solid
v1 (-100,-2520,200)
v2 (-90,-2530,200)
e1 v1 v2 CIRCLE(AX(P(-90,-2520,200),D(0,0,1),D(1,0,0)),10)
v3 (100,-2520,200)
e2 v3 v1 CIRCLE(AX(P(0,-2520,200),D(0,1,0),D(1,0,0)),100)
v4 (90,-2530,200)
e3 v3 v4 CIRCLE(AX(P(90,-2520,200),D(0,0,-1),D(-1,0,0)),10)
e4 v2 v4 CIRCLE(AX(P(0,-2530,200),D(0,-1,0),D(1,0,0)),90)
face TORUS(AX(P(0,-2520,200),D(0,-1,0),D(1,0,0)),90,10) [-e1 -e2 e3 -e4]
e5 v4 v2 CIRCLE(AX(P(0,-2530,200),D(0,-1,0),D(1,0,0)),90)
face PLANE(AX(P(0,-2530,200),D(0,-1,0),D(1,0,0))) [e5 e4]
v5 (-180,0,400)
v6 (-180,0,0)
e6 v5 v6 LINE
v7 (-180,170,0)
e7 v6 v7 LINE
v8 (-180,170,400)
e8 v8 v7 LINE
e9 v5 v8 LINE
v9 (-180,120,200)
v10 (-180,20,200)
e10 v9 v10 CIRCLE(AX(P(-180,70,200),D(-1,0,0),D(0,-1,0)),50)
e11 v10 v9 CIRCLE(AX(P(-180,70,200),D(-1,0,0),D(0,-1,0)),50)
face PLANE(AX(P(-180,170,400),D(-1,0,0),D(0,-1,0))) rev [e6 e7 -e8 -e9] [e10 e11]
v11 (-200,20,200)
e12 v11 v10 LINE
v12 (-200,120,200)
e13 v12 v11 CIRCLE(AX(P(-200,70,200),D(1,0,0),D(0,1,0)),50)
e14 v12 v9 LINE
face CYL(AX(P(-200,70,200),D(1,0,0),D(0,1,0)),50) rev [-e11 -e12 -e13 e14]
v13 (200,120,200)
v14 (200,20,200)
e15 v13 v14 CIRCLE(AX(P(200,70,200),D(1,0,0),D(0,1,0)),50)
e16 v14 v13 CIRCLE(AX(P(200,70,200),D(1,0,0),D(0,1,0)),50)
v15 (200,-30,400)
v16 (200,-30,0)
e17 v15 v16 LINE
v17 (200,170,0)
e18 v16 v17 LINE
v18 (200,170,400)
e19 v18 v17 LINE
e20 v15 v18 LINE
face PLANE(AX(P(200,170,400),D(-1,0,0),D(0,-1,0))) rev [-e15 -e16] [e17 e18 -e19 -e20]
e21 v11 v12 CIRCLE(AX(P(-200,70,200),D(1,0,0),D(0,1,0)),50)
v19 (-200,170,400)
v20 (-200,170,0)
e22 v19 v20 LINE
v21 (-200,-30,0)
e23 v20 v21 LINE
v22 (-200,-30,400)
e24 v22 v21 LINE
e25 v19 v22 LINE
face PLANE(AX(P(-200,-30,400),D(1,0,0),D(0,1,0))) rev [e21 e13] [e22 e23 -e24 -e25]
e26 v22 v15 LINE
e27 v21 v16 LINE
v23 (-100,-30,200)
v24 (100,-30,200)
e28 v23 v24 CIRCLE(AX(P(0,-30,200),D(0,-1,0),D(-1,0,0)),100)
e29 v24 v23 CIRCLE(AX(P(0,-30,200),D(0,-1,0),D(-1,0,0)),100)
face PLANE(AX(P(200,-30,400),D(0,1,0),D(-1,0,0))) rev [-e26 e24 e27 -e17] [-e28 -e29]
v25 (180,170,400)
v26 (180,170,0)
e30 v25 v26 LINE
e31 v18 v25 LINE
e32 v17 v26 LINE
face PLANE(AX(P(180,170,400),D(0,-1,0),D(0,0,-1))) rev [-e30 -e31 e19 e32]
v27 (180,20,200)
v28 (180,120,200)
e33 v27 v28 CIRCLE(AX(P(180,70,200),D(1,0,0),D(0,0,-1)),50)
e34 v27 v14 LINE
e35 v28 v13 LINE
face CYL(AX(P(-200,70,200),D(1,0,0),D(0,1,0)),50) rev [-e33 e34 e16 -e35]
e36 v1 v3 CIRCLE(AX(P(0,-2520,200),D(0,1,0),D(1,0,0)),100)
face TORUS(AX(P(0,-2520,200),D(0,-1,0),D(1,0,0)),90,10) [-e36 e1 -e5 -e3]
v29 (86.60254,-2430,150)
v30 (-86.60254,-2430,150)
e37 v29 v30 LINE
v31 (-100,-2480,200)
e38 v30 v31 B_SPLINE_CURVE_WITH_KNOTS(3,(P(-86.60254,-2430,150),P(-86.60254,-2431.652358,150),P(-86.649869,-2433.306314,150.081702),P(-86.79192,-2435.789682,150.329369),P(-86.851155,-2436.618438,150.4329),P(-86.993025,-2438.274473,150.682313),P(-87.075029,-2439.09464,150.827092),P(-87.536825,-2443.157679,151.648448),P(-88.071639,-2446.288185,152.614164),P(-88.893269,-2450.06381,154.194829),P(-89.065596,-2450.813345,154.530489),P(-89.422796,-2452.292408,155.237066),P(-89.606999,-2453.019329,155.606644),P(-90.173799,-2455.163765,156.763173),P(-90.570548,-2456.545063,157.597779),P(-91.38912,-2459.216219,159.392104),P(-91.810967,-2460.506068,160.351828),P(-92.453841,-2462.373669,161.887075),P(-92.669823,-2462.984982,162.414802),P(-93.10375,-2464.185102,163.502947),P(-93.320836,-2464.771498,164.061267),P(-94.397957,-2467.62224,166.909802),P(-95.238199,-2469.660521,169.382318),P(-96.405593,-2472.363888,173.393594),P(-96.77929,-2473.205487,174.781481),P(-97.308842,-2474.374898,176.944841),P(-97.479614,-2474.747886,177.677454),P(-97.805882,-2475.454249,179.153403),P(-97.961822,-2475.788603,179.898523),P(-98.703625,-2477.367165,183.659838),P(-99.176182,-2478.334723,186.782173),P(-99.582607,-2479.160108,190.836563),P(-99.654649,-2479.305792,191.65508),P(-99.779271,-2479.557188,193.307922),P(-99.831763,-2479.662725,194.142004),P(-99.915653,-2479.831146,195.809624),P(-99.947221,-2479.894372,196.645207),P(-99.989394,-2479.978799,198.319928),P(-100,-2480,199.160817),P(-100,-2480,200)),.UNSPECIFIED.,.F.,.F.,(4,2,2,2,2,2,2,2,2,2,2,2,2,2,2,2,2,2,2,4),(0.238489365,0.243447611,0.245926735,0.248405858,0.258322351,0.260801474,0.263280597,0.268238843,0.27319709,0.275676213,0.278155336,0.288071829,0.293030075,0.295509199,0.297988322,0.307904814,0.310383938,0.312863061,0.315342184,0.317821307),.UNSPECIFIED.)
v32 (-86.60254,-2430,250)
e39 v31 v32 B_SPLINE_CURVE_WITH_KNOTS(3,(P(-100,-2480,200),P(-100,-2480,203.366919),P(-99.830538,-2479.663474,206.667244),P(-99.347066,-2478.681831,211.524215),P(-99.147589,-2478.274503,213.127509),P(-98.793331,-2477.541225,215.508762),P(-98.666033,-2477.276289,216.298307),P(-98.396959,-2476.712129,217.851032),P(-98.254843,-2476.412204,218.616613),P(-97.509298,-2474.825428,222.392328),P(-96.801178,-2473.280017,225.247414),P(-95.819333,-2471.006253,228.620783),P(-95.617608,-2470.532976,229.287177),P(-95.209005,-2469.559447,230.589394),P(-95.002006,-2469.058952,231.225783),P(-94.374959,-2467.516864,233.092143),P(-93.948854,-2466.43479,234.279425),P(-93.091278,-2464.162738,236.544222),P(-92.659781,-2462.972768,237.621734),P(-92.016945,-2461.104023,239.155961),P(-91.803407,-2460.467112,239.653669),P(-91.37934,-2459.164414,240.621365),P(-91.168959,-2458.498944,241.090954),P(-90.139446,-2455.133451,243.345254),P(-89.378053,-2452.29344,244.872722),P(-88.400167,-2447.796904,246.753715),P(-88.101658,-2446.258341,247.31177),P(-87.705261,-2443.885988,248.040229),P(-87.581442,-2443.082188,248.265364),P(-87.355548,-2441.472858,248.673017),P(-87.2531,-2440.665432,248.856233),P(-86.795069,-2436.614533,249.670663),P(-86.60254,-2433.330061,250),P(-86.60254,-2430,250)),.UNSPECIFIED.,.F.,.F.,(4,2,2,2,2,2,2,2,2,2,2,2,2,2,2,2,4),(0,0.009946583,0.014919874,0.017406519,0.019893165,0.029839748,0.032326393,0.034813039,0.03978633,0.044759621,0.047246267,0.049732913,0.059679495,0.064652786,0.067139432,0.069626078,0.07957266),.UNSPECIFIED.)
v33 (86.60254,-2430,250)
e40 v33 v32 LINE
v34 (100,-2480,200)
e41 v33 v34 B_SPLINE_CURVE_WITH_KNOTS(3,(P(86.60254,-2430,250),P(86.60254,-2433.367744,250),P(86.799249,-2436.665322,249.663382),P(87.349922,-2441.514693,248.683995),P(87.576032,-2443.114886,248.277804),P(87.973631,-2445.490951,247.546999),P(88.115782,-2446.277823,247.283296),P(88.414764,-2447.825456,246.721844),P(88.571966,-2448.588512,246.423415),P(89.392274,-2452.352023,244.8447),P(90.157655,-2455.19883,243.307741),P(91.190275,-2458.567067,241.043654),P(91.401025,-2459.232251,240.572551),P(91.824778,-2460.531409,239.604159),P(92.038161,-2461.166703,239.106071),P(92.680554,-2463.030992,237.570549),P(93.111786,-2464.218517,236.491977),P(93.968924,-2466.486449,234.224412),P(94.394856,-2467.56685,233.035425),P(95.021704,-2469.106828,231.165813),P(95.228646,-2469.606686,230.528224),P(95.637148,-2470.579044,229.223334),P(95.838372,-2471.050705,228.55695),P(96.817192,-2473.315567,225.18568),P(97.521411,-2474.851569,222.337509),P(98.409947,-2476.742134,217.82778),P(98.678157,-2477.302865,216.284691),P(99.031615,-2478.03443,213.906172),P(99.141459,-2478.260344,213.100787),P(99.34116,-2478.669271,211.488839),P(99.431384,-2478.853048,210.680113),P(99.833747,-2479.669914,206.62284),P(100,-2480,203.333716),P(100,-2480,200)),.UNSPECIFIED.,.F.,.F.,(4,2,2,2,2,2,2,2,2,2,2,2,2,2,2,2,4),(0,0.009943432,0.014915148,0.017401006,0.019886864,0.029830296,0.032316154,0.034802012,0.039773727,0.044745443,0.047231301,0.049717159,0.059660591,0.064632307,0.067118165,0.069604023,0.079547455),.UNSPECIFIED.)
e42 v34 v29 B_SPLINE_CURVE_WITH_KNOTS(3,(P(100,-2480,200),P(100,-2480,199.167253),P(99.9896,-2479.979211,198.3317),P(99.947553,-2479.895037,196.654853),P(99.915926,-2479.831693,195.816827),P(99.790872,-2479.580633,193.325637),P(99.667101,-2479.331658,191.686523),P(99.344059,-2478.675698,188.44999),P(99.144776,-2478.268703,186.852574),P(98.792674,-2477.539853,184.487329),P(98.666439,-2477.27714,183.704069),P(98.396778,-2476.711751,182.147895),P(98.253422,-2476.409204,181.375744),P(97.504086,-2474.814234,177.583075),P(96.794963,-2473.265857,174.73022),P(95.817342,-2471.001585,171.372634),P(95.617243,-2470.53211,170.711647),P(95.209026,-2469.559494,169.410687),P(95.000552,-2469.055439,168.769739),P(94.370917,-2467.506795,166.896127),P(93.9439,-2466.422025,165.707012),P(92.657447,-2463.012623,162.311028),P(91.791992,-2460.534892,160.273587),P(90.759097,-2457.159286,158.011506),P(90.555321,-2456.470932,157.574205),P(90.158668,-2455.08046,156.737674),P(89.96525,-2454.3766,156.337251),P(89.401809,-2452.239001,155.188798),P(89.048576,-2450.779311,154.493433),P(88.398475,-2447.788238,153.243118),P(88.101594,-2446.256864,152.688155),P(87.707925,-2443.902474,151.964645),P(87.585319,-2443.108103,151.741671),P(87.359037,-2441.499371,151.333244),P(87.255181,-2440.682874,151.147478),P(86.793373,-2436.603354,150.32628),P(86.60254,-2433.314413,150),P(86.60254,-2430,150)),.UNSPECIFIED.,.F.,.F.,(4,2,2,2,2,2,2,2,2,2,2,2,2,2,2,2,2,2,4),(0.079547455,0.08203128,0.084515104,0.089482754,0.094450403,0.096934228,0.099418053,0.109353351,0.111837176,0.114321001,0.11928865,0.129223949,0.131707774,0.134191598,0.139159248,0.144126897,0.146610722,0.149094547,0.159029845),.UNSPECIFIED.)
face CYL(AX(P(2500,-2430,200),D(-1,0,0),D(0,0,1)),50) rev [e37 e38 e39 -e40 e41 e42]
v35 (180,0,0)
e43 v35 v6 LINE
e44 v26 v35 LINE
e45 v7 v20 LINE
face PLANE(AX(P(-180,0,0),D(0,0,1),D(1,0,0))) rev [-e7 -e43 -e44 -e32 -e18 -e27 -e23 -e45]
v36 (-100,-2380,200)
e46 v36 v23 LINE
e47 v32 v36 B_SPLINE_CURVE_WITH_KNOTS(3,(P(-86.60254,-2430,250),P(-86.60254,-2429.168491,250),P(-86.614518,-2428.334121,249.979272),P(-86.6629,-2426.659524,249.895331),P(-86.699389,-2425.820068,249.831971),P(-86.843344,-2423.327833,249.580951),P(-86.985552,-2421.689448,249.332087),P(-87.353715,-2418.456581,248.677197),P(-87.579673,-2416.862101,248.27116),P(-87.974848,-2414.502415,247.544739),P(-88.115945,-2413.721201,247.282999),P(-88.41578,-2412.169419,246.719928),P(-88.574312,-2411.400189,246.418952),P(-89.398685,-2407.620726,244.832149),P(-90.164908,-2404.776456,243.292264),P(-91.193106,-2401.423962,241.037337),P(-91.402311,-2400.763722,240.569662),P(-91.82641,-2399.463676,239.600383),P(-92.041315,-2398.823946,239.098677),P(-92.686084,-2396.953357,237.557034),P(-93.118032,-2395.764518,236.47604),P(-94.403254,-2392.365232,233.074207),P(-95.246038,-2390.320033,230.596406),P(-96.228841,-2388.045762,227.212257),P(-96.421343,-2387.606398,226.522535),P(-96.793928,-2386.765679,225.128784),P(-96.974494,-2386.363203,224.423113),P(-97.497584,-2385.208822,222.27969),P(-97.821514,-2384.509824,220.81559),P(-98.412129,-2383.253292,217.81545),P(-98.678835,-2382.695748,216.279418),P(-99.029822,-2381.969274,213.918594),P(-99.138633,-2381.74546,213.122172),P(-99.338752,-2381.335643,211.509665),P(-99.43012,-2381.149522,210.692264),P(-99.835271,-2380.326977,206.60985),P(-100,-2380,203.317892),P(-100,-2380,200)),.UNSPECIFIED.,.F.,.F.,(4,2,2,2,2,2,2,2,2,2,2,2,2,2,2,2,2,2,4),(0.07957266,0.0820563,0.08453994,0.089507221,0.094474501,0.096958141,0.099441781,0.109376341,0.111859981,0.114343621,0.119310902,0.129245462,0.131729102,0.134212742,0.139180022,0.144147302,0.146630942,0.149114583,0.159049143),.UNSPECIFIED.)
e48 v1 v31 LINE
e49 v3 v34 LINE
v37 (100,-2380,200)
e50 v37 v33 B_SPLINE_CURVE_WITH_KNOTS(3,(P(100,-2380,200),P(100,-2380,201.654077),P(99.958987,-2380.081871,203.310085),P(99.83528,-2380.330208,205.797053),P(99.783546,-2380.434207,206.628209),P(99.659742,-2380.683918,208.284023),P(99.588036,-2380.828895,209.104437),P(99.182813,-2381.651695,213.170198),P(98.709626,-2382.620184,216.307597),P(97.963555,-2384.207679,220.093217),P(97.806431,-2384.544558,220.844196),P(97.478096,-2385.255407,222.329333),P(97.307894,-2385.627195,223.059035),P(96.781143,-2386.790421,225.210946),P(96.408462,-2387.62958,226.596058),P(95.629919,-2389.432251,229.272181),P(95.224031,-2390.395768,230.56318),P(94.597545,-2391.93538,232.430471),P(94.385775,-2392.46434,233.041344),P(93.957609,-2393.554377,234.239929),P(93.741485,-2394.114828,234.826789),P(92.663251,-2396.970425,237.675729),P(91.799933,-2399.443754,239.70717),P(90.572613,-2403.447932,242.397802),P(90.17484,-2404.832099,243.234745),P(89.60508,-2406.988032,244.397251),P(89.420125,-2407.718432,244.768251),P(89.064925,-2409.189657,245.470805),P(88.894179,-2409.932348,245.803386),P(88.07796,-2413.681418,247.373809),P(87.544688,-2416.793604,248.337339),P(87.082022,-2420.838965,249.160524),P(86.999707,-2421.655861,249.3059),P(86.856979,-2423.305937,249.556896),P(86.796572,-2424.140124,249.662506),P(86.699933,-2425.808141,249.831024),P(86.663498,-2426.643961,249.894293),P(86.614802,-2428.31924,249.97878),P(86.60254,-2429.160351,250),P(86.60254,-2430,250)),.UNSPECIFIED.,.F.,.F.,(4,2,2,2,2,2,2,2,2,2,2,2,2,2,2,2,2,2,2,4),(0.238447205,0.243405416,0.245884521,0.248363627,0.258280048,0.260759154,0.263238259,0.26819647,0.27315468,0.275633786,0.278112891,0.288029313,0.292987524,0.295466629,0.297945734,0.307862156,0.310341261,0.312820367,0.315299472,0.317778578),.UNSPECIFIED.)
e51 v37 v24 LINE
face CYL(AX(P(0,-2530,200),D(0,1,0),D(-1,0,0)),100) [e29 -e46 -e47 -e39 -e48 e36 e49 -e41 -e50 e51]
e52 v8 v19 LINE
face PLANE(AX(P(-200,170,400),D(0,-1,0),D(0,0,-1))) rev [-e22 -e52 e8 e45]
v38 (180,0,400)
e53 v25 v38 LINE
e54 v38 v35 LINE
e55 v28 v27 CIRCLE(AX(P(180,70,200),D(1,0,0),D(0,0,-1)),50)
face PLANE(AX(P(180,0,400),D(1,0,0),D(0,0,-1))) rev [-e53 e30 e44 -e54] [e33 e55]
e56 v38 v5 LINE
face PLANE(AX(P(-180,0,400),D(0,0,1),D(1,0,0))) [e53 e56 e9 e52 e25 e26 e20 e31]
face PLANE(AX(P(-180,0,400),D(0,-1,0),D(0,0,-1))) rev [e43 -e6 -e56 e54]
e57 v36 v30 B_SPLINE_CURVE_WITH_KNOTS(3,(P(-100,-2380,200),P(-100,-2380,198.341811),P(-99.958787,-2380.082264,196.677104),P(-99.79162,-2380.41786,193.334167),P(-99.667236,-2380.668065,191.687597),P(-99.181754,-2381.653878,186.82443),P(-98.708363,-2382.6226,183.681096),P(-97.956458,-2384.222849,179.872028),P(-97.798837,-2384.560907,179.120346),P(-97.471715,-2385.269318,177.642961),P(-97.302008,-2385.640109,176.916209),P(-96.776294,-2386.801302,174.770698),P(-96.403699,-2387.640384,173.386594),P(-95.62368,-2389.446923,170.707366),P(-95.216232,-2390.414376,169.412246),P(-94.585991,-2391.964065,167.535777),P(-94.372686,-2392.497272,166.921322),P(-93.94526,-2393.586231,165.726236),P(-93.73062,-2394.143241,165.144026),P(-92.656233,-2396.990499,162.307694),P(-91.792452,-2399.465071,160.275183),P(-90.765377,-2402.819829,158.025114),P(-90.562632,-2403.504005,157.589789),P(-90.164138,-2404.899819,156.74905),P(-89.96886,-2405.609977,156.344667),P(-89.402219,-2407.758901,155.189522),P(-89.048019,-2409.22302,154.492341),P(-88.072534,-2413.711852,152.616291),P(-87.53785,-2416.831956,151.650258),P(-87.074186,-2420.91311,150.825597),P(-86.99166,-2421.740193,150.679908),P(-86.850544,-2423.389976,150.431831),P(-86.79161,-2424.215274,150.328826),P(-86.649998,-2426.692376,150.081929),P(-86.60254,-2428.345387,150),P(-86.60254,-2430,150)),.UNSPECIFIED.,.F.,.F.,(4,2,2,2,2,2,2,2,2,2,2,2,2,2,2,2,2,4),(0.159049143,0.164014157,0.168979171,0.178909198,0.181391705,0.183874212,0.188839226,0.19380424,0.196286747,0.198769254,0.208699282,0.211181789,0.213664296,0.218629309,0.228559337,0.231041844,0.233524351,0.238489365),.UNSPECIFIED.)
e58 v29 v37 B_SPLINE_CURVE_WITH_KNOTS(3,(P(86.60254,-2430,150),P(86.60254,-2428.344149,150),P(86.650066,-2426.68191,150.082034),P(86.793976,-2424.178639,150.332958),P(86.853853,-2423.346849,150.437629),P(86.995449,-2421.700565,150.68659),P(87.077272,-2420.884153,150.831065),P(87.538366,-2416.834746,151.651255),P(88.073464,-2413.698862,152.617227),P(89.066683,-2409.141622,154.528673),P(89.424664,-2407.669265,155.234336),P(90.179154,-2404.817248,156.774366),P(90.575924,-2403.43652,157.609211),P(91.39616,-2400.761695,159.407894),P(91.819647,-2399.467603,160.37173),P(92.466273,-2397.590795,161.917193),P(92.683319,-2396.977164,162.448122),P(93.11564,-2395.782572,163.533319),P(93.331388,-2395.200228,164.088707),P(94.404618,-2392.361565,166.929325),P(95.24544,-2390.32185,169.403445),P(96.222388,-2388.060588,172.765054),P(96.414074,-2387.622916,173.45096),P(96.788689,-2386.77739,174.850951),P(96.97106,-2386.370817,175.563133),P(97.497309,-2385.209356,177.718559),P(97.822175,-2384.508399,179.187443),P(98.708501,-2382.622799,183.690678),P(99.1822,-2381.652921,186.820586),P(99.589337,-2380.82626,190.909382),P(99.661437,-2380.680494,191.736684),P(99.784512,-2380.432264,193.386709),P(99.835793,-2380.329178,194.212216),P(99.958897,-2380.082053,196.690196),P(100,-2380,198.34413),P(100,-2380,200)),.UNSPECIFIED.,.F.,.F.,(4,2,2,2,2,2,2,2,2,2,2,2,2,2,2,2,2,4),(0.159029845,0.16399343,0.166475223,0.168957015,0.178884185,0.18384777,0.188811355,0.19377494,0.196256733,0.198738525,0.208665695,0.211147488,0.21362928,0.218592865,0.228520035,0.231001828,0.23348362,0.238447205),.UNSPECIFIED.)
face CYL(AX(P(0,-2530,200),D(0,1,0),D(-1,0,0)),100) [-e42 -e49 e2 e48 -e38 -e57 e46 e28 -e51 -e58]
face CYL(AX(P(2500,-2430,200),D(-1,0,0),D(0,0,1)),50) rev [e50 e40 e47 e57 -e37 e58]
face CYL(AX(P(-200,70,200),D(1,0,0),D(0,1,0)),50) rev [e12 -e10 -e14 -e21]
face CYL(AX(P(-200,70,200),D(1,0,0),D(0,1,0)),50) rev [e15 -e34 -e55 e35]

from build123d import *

# Parameters (mm, degrees)
BOSS_EXTRUDE1_DEPTH     = 400
SKETCH2_R               = 50
CUT_EXTRUDE1_DEPTH      = 400
SKETCH3_R               = 100
BOSS_EXTRUDE2_DEPTH     = 2500
CUT_EXTRUDE2_DEPTH      = 2500
CUT_EXTRUDE2_DEPTH_BACK = 2500
SKETCH4_R               = 50
FILLET1_R               = 10


with BuildPart() as part:
    # Sketch1 → Boss-Extrude1 (new body)
    with BuildSketch(Plane.XY):
        Polygon((-180, 0), (180, 0), (180, 170), (200, 170), (200, -30), (-200, -30), (-200, 170), (-180, 170), align=None)
    extrude(amount=BOSS_EXTRUDE1_DEPTH)

    # Sketch2 → Cut-Extrude1 (cut)
    with BuildSketch(Plane(origin=(200, 0, 0), x_dir=(0, 0, -1), z_dir=(1, 0, 0))):
        with Locations(Location((-200, 70, 0), (0, 0, 90))):
            Circle(SKETCH2_R)
    extrude(amount=-CUT_EXTRUDE1_DEPTH, mode=Mode.SUBTRACT)

    # Sketch3 → Boss-Extrude2 (add)
    with BuildSketch(Plane.XZ.offset(30)):
        with Locations(Location((0, 200, 0), (0, 0, 180))):
            Circle(SKETCH3_R)
    extrude(amount=BOSS_EXTRUDE2_DEPTH)

    # Sketch4 → Cut-Extrude2 (cut, two sides: drawn at the far end of the back side and taken through both)
    with BuildSketch(Plane(origin=(0, 0, 0), x_dir=(0, 0, -1), z_dir=(1, 0, 0)).offset(-CUT_EXTRUDE2_DEPTH_BACK)):
        with Locations(Location((-200, -2430, 0), (0, 0, 180))):
            Circle(SKETCH4_R)
    extrude(amount=CUT_EXTRUDE2_DEPTH + CUT_EXTRUDE2_DEPTH_BACK, mode=Mode.SUBTRACT)

    # Fillet1
    fillet1_edges = [part.edges().sort_by_distance(p)[0] for p in [
        (100, -2530, 200),
    ]]
    fillet(fillet1_edges, radius=FILLET1_R)


solid = part.part
